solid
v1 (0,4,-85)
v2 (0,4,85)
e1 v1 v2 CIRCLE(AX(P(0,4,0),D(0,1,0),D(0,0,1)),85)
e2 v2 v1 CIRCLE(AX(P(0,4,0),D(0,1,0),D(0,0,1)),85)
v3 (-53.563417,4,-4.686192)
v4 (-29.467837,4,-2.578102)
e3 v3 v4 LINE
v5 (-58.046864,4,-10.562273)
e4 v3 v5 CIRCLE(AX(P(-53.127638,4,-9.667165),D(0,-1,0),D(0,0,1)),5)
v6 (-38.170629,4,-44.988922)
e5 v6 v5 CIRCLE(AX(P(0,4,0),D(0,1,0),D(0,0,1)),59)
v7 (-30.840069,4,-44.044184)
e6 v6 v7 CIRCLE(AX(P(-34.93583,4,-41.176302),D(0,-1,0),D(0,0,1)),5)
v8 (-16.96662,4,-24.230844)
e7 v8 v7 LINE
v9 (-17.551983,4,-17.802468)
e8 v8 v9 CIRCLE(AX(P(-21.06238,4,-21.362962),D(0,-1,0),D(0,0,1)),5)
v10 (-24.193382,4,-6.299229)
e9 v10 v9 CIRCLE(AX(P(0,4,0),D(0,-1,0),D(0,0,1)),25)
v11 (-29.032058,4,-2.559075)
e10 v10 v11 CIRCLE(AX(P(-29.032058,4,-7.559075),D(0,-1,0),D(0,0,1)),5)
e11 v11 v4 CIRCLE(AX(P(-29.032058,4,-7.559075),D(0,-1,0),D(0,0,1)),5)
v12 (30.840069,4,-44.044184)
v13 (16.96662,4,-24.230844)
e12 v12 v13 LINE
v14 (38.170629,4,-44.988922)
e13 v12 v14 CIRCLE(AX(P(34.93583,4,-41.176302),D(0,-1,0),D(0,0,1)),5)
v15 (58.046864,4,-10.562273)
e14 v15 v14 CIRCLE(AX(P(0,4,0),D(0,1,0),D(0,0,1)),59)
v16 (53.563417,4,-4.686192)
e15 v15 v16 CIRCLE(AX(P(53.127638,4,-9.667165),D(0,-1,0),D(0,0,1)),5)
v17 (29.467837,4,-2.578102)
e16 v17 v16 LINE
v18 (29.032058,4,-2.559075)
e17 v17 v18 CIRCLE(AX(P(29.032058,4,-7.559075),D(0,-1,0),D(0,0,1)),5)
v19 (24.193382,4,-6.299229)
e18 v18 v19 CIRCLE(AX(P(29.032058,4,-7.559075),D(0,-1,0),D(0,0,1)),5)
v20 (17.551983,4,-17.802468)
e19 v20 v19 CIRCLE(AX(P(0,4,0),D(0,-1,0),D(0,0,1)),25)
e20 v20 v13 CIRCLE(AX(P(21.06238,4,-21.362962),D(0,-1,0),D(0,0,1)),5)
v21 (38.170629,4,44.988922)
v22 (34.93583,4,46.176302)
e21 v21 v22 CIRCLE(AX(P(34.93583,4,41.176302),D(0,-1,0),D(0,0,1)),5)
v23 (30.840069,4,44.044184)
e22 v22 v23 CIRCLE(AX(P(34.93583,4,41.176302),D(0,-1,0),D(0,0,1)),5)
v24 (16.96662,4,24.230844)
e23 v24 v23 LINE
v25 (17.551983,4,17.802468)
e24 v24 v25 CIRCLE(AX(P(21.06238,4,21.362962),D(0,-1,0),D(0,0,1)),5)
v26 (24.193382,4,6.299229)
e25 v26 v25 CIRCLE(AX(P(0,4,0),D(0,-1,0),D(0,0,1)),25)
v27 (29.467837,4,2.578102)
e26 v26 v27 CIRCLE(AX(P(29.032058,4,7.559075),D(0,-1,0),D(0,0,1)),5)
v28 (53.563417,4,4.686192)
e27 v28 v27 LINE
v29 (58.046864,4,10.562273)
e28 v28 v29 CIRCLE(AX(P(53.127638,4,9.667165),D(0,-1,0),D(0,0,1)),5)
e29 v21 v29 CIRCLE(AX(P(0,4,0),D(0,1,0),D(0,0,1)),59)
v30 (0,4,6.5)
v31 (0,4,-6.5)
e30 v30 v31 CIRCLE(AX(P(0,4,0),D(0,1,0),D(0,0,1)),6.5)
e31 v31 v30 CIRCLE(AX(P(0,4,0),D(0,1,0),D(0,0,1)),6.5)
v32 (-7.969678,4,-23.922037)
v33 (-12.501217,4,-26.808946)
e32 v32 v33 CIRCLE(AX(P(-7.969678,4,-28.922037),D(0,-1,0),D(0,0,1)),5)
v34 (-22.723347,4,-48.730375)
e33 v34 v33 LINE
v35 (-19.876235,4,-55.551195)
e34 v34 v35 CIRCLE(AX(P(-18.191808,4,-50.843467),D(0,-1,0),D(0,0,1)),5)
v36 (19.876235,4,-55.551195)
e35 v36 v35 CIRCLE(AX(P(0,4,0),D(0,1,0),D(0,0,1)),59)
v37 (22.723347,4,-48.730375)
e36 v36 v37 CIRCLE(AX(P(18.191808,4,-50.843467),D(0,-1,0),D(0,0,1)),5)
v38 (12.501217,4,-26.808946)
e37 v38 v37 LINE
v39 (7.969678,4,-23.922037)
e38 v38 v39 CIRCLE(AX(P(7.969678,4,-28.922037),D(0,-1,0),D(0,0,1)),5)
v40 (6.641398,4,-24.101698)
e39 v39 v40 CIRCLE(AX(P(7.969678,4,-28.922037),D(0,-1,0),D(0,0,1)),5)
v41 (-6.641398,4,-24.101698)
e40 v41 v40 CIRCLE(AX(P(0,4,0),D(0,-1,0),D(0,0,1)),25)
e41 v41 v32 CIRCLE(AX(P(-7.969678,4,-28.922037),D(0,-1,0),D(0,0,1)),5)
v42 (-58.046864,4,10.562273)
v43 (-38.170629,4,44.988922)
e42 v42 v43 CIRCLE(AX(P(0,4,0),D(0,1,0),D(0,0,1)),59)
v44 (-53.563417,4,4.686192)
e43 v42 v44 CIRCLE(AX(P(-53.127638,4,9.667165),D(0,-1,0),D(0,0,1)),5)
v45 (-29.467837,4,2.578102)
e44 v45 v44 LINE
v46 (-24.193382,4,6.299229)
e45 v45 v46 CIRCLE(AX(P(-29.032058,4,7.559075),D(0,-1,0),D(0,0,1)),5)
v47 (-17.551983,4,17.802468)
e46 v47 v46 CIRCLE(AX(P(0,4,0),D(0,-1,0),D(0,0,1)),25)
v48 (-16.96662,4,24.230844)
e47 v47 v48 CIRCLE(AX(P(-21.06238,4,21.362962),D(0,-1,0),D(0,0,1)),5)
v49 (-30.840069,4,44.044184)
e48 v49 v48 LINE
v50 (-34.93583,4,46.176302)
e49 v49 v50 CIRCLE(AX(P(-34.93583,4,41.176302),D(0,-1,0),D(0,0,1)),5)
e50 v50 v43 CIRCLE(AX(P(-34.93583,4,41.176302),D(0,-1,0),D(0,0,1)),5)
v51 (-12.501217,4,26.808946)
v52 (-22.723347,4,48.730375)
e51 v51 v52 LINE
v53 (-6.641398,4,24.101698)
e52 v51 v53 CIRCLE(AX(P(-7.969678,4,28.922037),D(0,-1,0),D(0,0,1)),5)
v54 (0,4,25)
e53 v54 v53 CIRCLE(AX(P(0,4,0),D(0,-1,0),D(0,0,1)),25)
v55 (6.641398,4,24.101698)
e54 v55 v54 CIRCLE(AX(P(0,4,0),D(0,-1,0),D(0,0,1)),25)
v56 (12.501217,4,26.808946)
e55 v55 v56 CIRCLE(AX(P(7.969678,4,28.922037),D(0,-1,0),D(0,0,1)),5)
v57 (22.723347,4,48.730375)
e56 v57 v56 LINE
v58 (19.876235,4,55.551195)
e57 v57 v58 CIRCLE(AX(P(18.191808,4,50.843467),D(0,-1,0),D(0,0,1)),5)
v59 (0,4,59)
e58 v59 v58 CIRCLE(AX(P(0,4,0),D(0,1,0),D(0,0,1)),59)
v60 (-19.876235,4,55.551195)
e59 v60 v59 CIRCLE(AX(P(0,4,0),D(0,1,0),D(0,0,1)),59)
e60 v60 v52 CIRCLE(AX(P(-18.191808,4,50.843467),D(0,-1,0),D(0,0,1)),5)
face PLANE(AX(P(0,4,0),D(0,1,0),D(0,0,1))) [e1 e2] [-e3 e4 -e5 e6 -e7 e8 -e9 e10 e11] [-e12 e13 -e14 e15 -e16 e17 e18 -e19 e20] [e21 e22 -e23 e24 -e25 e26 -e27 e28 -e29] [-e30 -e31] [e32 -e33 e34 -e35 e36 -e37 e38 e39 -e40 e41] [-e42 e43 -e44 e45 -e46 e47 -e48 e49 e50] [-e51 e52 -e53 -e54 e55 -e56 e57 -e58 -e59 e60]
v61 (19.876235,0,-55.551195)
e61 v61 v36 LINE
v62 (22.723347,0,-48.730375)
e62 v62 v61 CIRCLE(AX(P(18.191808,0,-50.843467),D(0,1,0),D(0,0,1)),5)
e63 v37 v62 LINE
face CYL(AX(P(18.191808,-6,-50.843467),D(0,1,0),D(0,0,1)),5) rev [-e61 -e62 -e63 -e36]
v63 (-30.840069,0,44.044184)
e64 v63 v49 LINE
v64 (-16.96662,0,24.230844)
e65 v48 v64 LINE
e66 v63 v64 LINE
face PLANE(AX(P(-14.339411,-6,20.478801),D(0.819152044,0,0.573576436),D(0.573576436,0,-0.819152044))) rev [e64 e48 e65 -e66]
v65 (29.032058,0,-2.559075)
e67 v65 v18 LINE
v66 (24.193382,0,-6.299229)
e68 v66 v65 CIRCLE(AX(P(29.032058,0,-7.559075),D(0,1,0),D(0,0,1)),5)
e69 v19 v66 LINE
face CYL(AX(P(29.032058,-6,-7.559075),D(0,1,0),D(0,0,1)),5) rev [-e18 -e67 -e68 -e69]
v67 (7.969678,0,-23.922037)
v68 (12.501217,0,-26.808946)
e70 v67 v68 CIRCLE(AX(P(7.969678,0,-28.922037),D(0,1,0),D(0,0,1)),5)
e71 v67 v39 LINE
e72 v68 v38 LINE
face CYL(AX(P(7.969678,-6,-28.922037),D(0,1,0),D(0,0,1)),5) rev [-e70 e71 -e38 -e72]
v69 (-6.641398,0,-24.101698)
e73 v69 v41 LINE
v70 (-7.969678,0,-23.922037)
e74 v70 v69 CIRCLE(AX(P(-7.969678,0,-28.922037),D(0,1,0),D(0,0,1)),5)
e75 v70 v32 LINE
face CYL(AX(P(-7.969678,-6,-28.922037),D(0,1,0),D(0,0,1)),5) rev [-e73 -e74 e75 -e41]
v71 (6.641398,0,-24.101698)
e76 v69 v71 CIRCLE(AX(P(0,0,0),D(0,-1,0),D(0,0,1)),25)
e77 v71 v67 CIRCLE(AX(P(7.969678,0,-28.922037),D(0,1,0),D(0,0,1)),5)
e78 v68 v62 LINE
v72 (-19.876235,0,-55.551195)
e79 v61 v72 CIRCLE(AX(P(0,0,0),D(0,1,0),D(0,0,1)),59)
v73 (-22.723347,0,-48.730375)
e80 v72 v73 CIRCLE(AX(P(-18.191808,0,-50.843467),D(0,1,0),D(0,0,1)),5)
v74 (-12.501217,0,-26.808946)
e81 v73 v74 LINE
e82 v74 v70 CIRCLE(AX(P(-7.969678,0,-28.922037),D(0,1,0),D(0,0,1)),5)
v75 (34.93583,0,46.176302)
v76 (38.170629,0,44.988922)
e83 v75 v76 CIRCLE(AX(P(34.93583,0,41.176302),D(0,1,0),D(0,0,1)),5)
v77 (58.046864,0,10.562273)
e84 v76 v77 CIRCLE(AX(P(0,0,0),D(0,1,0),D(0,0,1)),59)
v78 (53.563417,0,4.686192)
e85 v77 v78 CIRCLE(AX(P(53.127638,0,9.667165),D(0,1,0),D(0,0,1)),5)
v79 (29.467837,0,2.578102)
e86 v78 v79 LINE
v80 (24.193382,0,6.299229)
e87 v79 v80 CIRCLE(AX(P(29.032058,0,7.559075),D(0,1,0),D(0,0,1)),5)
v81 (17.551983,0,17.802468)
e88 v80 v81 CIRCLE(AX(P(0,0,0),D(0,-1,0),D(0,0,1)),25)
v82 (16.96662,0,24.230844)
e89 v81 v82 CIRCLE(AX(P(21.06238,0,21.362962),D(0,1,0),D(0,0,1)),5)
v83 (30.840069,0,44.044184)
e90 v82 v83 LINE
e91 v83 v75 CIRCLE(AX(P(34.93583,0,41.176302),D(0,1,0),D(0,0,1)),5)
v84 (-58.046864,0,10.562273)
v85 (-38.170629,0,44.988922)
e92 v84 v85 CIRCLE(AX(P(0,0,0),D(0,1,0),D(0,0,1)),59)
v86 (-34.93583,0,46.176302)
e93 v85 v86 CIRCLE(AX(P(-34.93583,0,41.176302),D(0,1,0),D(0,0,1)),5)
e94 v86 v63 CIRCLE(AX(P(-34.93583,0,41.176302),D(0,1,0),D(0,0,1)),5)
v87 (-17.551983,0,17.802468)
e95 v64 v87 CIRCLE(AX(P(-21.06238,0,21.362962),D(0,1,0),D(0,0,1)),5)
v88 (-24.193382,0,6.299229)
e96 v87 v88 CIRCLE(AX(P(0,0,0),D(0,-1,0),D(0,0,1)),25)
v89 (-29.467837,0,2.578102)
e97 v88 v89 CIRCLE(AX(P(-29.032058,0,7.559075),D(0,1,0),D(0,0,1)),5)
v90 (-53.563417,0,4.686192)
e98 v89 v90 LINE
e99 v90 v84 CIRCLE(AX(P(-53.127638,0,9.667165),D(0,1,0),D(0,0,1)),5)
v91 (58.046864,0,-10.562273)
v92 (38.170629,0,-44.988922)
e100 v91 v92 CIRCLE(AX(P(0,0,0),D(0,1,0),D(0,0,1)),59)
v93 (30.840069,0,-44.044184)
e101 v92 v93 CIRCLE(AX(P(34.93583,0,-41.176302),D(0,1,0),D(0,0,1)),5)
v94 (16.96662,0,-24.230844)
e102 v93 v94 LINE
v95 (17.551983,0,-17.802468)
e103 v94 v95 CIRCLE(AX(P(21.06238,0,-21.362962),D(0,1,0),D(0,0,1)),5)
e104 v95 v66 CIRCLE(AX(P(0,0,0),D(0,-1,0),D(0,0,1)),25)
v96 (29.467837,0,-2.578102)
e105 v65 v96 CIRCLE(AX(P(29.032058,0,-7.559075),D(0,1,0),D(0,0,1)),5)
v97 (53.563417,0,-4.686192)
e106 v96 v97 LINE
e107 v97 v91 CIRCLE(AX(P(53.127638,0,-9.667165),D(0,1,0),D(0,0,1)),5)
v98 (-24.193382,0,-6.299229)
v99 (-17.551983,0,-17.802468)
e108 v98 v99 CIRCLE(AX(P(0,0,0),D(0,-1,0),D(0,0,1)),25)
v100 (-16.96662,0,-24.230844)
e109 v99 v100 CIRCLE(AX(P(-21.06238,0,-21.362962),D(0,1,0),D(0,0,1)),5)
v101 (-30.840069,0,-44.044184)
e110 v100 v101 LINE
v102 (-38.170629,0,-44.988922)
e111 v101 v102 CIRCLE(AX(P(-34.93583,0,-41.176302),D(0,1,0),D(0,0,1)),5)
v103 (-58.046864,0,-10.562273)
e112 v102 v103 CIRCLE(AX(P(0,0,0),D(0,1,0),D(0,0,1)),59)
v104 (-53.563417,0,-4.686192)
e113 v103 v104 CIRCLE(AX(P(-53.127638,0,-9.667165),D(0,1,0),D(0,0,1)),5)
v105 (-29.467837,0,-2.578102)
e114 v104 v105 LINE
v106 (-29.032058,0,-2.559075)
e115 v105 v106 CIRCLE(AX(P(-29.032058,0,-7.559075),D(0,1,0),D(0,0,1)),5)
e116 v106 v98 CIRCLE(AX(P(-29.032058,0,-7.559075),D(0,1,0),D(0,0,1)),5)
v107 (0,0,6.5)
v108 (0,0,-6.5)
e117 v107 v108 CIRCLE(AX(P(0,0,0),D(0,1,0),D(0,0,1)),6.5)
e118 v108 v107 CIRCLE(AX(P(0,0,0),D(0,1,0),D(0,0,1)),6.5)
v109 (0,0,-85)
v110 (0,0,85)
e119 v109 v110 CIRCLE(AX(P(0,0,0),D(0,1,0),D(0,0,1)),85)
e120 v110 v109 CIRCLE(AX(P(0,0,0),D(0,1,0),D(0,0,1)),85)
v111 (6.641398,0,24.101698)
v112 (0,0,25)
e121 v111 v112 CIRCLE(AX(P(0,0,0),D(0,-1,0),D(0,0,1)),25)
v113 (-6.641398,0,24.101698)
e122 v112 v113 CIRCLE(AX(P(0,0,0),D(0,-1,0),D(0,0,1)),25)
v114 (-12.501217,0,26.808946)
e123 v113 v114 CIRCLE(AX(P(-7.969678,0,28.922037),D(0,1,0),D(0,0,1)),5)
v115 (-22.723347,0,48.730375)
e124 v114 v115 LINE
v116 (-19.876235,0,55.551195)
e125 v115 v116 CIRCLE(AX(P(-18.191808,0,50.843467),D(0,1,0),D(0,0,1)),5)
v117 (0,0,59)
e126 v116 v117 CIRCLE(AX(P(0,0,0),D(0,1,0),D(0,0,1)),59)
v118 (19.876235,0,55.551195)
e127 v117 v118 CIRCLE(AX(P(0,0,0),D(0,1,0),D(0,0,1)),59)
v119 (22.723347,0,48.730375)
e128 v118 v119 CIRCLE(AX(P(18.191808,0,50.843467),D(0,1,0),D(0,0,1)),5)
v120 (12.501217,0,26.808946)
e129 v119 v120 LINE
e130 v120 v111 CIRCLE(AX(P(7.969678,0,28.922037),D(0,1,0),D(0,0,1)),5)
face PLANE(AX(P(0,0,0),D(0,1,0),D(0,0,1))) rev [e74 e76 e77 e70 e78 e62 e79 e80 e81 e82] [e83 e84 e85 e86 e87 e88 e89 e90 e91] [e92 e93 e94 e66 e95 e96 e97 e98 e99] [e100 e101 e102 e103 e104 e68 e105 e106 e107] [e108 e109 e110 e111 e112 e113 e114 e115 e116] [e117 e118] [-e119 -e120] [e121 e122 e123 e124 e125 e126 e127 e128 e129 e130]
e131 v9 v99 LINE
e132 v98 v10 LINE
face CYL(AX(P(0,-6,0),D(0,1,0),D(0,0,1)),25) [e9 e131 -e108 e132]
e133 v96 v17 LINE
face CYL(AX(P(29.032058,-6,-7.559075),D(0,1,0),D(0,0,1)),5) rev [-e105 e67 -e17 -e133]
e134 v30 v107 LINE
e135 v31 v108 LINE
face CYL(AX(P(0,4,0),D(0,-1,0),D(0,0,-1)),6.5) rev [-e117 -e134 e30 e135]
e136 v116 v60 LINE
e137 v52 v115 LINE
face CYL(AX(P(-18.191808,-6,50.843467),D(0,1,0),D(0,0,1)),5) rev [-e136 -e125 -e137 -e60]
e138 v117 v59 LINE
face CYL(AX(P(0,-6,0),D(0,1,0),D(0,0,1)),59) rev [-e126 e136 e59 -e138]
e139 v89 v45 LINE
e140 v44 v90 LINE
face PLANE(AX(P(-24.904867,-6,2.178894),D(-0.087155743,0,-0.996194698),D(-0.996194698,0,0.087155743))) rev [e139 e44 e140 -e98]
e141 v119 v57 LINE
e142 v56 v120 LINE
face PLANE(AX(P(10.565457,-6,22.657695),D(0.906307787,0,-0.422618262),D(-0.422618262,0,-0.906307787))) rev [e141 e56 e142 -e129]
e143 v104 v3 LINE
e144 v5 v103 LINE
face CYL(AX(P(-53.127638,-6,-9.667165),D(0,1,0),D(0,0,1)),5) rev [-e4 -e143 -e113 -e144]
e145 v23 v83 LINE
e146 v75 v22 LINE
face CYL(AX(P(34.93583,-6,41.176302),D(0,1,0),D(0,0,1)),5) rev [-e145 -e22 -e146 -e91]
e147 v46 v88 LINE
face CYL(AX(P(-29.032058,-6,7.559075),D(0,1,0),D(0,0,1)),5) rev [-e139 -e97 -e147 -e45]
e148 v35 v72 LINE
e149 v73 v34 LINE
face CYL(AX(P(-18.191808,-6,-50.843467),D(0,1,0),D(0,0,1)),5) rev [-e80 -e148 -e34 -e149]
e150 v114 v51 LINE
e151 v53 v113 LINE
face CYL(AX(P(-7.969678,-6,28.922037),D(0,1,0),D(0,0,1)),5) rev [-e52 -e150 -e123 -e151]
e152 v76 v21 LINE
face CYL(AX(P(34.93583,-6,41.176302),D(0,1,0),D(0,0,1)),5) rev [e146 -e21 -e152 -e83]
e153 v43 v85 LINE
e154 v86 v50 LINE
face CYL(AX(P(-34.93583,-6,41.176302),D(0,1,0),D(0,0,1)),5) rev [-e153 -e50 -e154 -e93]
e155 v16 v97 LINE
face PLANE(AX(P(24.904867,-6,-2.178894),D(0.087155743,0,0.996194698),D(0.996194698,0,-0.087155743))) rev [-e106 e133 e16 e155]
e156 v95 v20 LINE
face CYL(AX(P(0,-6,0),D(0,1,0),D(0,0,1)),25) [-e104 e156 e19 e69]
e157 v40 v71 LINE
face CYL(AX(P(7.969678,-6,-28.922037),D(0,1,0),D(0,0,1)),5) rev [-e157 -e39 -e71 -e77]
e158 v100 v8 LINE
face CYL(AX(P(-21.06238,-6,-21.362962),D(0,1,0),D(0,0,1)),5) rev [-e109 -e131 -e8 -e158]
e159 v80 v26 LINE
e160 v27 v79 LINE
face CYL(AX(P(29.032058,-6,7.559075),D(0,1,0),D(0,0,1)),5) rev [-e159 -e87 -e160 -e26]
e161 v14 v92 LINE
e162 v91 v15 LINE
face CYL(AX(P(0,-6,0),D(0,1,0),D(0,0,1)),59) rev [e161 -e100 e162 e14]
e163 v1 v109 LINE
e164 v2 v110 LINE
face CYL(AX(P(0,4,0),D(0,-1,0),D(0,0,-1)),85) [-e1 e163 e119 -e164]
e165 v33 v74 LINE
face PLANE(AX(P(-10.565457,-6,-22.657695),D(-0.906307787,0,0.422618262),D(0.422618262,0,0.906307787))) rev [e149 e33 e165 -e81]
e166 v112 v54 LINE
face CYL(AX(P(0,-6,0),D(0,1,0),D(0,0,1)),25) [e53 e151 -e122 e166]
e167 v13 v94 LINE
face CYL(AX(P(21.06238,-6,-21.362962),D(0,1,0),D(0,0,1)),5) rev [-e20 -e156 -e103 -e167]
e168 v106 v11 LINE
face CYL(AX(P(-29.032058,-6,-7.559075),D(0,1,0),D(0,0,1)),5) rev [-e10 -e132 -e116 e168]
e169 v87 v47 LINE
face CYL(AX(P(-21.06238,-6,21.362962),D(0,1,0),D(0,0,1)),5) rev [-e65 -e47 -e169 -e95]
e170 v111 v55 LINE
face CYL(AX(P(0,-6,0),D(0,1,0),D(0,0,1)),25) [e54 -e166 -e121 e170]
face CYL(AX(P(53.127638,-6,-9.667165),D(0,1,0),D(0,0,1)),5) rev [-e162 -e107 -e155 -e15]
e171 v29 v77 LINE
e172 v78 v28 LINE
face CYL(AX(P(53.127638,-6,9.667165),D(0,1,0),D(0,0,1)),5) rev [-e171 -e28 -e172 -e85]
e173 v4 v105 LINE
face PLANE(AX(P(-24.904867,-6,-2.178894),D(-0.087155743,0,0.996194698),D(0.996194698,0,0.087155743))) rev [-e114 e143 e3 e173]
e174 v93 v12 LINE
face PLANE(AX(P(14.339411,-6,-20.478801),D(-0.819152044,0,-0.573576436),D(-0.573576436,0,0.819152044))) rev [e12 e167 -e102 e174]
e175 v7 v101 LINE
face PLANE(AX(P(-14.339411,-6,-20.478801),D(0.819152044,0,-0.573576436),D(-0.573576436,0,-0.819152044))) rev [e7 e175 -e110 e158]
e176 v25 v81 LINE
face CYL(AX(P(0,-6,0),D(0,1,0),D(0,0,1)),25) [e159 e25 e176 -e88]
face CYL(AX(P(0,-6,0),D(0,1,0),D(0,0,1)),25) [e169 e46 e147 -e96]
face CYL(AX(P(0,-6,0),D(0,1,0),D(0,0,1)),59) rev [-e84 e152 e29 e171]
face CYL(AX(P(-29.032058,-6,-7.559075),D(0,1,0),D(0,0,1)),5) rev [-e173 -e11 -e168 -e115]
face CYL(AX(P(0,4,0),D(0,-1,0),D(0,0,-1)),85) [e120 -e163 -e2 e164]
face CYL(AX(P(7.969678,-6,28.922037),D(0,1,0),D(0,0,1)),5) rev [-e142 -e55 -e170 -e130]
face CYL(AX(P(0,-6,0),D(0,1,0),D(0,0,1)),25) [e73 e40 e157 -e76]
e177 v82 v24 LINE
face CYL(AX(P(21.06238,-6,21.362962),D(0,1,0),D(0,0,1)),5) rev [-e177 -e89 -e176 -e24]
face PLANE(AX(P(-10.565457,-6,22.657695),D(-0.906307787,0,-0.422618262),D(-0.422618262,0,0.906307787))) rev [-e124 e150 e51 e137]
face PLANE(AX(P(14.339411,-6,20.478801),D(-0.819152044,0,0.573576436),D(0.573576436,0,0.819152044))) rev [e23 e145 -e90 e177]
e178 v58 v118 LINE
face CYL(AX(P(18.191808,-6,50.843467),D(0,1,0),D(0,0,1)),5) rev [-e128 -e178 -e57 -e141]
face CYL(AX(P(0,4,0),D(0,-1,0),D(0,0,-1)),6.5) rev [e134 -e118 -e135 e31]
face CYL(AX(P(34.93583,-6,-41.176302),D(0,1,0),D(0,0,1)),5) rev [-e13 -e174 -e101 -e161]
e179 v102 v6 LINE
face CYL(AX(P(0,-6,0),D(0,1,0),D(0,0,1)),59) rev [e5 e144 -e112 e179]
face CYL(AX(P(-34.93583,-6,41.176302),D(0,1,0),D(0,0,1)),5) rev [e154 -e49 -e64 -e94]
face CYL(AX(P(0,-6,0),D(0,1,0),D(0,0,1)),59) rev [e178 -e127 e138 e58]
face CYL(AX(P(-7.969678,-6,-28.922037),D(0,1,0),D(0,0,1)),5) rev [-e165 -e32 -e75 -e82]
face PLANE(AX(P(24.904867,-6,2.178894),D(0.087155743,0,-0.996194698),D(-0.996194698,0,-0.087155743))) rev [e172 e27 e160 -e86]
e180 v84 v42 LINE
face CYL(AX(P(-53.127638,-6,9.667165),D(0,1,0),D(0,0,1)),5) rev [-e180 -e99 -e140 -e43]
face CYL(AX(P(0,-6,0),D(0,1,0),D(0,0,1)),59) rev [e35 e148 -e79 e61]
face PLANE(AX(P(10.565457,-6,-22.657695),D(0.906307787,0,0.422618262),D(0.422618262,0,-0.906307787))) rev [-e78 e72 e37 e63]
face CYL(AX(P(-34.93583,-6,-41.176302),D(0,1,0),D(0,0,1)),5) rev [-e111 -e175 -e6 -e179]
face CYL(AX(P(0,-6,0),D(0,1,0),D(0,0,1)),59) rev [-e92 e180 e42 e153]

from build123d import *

# Parameters (mm, degrees)
SKETCH1_R           = 85
SKETCH1_R_2         = 6.5
BOSS_EXTRUDE1_DEPTH = 4
CUT_EXTRUDE1_DEPTH  = 10
FILLET1_R           = 5


with BuildPart() as part:
    # Sketch1 → Boss-Extrude1 (new body)
    with BuildSketch(Plane(origin=(0, 0, 0), x_dir=(1, 0, 0), z_dir=(0, 1, 0))):
        with Locations(Location((0, 0, 0), (0, 0, 270))):
            Circle(SKETCH1_R)
        with Locations(Location((0, 0, 0), (0, 0, 270))):
            Circle(SKETCH1_R_2, mode=Mode.SUBTRACT)
    extrude(amount=BOSS_EXTRUDE1_DEPTH)

    # Sketch2 → Cut-Extrude1 (cut)
    with BuildSketch(Plane(origin=(0, 4, 0), x_dir=(1, 0, 0), z_dir=(0, 1, 0))):
        with BuildLine():
            Line((10.565456544, 22.657694676), (24.934477443, 53.472159435))
            ThreePointArc((24.934477443, 53.472159435), (0, 59), (-24.934477443, 53.472159435))
            Line((-24.934477443, 53.472159435), (-10.565456544, 22.657694676))
            ThreePointArc((-10.565456544, 22.657694676), (0, 25), (10.565456544, 22.657694676))
        make_face()
        with BuildLine():
            Line((14.339410909, 20.478801107), (33.841009745, 48.329970613))
            ThreePointArc((33.841009745, 48.329970613), (51.095498823, 29.5), (58.775487187, 5.142188822))
            Line((58.775487187, 5.142188822), (24.904867452, 2.178893569))
            ThreePointArc((24.904867452, 2.178893569), (21.650635095, 12.5), (14.339410909, 20.478801107))
        make_face()
        with BuildLine():
            Line((24.904867452, -2.178893569), (58.775487187, -5.142188822))
            ThreePointArc((58.775487187, -5.142188822), (51.095498823, -29.5), (33.841009745, -48.329970613))
            Line((33.841009745, -48.329970613), (14.339410909, -20.478801107))
            ThreePointArc((14.339410909, -20.478801107), (21.650635095, -12.5), (24.904867452, -2.178893569))
        make_face()
        with BuildLine():
            Line((10.565456544, -22.657694676), (24.934477443, -53.472159435))
            ThreePointArc((24.934477443, -53.472159435), (0, -59), (-24.934477443, -53.472159435))
            Line((-24.934477443, -53.472159435), (-10.565456544, -22.657694676))
            ThreePointArc((-10.565456544, -22.657694676), (0, -25), (10.565456544, -22.657694676))
        make_face()
        with BuildLine():
            Line((-14.339410909, -20.478801107), (-33.841009745, -48.329970613))
            ThreePointArc((-33.841009745, -48.329970613), (-51.095498823, -29.5), (-58.775487187, -5.142188822))
            Line((-58.775487187, -5.142188822), (-24.904867452, -2.178893569))
            ThreePointArc((-24.904867452, -2.178893569), (-21.650635095, -12.5), (-14.339410909, -20.478801107))
        make_face()
        with BuildLine():
            Line((-24.904867452, 2.178893569), (-58.775487187, 5.142188822))
            ThreePointArc((-58.775487187, 5.142188822), (-51.095498823, 29.5), (-33.841009745, 48.329970613))
            Line((-33.841009745, 48.329970613), (-14.339410909, 20.478801107))
            ThreePointArc((-14.339410909, 20.478801107), (-21.650635095, 12.5), (-24.904867452, 2.178893569))
        make_face()
    extrude(amount=-CUT_EXTRUDE1_DEPTH, mode=Mode.SUBTRACT)

    # Fillet1
    fillet1_edges = [part.edges().sort_by_distance(p)[0] for p in [
        (-10.565456544, 2, 22.657694676),
        (10.565456544, 2, 22.657694676),
        (24.934477443, 2, 53.472159435),
        (-24.934477443, 2, 53.472159435),
        (-24.904867452, 2, 2.178893569),
        (-14.339410909, 2, 20.478801107),
        (-33.841009745, 2, 48.329970613),
        (-58.775487187, 2, 5.142188822),
        (14.339410909, 2, 20.478801107),
        (24.904867452, 2, 2.178893569),
        (58.775487187, 2, 5.142188822),
        (33.841009745, 2, 48.329970613),
        (24.904867452, 2, -2.178893569),
        (14.339410909, 2, -20.478801107),
        (33.841009745, 2, -48.329970613),
        (58.775487187, 2, -5.142188822),
        (-14.339410909, 2, -20.478801107),
        (-24.904867452, 2, -2.178893569),
        (-58.775487187, 2, -5.142188822),
        (-33.841009745, 2, -48.329970613),
        (10.565456544, 2, -22.657694676),
        (-10.565456544, 2, -22.657694676),
        (-24.934477443, 2, -53.472159435),
        (24.934477443, 2, -53.472159435),
    ]]
    fillet(fillet1_edges, radius=FILLET1_R)


solid = part.part
